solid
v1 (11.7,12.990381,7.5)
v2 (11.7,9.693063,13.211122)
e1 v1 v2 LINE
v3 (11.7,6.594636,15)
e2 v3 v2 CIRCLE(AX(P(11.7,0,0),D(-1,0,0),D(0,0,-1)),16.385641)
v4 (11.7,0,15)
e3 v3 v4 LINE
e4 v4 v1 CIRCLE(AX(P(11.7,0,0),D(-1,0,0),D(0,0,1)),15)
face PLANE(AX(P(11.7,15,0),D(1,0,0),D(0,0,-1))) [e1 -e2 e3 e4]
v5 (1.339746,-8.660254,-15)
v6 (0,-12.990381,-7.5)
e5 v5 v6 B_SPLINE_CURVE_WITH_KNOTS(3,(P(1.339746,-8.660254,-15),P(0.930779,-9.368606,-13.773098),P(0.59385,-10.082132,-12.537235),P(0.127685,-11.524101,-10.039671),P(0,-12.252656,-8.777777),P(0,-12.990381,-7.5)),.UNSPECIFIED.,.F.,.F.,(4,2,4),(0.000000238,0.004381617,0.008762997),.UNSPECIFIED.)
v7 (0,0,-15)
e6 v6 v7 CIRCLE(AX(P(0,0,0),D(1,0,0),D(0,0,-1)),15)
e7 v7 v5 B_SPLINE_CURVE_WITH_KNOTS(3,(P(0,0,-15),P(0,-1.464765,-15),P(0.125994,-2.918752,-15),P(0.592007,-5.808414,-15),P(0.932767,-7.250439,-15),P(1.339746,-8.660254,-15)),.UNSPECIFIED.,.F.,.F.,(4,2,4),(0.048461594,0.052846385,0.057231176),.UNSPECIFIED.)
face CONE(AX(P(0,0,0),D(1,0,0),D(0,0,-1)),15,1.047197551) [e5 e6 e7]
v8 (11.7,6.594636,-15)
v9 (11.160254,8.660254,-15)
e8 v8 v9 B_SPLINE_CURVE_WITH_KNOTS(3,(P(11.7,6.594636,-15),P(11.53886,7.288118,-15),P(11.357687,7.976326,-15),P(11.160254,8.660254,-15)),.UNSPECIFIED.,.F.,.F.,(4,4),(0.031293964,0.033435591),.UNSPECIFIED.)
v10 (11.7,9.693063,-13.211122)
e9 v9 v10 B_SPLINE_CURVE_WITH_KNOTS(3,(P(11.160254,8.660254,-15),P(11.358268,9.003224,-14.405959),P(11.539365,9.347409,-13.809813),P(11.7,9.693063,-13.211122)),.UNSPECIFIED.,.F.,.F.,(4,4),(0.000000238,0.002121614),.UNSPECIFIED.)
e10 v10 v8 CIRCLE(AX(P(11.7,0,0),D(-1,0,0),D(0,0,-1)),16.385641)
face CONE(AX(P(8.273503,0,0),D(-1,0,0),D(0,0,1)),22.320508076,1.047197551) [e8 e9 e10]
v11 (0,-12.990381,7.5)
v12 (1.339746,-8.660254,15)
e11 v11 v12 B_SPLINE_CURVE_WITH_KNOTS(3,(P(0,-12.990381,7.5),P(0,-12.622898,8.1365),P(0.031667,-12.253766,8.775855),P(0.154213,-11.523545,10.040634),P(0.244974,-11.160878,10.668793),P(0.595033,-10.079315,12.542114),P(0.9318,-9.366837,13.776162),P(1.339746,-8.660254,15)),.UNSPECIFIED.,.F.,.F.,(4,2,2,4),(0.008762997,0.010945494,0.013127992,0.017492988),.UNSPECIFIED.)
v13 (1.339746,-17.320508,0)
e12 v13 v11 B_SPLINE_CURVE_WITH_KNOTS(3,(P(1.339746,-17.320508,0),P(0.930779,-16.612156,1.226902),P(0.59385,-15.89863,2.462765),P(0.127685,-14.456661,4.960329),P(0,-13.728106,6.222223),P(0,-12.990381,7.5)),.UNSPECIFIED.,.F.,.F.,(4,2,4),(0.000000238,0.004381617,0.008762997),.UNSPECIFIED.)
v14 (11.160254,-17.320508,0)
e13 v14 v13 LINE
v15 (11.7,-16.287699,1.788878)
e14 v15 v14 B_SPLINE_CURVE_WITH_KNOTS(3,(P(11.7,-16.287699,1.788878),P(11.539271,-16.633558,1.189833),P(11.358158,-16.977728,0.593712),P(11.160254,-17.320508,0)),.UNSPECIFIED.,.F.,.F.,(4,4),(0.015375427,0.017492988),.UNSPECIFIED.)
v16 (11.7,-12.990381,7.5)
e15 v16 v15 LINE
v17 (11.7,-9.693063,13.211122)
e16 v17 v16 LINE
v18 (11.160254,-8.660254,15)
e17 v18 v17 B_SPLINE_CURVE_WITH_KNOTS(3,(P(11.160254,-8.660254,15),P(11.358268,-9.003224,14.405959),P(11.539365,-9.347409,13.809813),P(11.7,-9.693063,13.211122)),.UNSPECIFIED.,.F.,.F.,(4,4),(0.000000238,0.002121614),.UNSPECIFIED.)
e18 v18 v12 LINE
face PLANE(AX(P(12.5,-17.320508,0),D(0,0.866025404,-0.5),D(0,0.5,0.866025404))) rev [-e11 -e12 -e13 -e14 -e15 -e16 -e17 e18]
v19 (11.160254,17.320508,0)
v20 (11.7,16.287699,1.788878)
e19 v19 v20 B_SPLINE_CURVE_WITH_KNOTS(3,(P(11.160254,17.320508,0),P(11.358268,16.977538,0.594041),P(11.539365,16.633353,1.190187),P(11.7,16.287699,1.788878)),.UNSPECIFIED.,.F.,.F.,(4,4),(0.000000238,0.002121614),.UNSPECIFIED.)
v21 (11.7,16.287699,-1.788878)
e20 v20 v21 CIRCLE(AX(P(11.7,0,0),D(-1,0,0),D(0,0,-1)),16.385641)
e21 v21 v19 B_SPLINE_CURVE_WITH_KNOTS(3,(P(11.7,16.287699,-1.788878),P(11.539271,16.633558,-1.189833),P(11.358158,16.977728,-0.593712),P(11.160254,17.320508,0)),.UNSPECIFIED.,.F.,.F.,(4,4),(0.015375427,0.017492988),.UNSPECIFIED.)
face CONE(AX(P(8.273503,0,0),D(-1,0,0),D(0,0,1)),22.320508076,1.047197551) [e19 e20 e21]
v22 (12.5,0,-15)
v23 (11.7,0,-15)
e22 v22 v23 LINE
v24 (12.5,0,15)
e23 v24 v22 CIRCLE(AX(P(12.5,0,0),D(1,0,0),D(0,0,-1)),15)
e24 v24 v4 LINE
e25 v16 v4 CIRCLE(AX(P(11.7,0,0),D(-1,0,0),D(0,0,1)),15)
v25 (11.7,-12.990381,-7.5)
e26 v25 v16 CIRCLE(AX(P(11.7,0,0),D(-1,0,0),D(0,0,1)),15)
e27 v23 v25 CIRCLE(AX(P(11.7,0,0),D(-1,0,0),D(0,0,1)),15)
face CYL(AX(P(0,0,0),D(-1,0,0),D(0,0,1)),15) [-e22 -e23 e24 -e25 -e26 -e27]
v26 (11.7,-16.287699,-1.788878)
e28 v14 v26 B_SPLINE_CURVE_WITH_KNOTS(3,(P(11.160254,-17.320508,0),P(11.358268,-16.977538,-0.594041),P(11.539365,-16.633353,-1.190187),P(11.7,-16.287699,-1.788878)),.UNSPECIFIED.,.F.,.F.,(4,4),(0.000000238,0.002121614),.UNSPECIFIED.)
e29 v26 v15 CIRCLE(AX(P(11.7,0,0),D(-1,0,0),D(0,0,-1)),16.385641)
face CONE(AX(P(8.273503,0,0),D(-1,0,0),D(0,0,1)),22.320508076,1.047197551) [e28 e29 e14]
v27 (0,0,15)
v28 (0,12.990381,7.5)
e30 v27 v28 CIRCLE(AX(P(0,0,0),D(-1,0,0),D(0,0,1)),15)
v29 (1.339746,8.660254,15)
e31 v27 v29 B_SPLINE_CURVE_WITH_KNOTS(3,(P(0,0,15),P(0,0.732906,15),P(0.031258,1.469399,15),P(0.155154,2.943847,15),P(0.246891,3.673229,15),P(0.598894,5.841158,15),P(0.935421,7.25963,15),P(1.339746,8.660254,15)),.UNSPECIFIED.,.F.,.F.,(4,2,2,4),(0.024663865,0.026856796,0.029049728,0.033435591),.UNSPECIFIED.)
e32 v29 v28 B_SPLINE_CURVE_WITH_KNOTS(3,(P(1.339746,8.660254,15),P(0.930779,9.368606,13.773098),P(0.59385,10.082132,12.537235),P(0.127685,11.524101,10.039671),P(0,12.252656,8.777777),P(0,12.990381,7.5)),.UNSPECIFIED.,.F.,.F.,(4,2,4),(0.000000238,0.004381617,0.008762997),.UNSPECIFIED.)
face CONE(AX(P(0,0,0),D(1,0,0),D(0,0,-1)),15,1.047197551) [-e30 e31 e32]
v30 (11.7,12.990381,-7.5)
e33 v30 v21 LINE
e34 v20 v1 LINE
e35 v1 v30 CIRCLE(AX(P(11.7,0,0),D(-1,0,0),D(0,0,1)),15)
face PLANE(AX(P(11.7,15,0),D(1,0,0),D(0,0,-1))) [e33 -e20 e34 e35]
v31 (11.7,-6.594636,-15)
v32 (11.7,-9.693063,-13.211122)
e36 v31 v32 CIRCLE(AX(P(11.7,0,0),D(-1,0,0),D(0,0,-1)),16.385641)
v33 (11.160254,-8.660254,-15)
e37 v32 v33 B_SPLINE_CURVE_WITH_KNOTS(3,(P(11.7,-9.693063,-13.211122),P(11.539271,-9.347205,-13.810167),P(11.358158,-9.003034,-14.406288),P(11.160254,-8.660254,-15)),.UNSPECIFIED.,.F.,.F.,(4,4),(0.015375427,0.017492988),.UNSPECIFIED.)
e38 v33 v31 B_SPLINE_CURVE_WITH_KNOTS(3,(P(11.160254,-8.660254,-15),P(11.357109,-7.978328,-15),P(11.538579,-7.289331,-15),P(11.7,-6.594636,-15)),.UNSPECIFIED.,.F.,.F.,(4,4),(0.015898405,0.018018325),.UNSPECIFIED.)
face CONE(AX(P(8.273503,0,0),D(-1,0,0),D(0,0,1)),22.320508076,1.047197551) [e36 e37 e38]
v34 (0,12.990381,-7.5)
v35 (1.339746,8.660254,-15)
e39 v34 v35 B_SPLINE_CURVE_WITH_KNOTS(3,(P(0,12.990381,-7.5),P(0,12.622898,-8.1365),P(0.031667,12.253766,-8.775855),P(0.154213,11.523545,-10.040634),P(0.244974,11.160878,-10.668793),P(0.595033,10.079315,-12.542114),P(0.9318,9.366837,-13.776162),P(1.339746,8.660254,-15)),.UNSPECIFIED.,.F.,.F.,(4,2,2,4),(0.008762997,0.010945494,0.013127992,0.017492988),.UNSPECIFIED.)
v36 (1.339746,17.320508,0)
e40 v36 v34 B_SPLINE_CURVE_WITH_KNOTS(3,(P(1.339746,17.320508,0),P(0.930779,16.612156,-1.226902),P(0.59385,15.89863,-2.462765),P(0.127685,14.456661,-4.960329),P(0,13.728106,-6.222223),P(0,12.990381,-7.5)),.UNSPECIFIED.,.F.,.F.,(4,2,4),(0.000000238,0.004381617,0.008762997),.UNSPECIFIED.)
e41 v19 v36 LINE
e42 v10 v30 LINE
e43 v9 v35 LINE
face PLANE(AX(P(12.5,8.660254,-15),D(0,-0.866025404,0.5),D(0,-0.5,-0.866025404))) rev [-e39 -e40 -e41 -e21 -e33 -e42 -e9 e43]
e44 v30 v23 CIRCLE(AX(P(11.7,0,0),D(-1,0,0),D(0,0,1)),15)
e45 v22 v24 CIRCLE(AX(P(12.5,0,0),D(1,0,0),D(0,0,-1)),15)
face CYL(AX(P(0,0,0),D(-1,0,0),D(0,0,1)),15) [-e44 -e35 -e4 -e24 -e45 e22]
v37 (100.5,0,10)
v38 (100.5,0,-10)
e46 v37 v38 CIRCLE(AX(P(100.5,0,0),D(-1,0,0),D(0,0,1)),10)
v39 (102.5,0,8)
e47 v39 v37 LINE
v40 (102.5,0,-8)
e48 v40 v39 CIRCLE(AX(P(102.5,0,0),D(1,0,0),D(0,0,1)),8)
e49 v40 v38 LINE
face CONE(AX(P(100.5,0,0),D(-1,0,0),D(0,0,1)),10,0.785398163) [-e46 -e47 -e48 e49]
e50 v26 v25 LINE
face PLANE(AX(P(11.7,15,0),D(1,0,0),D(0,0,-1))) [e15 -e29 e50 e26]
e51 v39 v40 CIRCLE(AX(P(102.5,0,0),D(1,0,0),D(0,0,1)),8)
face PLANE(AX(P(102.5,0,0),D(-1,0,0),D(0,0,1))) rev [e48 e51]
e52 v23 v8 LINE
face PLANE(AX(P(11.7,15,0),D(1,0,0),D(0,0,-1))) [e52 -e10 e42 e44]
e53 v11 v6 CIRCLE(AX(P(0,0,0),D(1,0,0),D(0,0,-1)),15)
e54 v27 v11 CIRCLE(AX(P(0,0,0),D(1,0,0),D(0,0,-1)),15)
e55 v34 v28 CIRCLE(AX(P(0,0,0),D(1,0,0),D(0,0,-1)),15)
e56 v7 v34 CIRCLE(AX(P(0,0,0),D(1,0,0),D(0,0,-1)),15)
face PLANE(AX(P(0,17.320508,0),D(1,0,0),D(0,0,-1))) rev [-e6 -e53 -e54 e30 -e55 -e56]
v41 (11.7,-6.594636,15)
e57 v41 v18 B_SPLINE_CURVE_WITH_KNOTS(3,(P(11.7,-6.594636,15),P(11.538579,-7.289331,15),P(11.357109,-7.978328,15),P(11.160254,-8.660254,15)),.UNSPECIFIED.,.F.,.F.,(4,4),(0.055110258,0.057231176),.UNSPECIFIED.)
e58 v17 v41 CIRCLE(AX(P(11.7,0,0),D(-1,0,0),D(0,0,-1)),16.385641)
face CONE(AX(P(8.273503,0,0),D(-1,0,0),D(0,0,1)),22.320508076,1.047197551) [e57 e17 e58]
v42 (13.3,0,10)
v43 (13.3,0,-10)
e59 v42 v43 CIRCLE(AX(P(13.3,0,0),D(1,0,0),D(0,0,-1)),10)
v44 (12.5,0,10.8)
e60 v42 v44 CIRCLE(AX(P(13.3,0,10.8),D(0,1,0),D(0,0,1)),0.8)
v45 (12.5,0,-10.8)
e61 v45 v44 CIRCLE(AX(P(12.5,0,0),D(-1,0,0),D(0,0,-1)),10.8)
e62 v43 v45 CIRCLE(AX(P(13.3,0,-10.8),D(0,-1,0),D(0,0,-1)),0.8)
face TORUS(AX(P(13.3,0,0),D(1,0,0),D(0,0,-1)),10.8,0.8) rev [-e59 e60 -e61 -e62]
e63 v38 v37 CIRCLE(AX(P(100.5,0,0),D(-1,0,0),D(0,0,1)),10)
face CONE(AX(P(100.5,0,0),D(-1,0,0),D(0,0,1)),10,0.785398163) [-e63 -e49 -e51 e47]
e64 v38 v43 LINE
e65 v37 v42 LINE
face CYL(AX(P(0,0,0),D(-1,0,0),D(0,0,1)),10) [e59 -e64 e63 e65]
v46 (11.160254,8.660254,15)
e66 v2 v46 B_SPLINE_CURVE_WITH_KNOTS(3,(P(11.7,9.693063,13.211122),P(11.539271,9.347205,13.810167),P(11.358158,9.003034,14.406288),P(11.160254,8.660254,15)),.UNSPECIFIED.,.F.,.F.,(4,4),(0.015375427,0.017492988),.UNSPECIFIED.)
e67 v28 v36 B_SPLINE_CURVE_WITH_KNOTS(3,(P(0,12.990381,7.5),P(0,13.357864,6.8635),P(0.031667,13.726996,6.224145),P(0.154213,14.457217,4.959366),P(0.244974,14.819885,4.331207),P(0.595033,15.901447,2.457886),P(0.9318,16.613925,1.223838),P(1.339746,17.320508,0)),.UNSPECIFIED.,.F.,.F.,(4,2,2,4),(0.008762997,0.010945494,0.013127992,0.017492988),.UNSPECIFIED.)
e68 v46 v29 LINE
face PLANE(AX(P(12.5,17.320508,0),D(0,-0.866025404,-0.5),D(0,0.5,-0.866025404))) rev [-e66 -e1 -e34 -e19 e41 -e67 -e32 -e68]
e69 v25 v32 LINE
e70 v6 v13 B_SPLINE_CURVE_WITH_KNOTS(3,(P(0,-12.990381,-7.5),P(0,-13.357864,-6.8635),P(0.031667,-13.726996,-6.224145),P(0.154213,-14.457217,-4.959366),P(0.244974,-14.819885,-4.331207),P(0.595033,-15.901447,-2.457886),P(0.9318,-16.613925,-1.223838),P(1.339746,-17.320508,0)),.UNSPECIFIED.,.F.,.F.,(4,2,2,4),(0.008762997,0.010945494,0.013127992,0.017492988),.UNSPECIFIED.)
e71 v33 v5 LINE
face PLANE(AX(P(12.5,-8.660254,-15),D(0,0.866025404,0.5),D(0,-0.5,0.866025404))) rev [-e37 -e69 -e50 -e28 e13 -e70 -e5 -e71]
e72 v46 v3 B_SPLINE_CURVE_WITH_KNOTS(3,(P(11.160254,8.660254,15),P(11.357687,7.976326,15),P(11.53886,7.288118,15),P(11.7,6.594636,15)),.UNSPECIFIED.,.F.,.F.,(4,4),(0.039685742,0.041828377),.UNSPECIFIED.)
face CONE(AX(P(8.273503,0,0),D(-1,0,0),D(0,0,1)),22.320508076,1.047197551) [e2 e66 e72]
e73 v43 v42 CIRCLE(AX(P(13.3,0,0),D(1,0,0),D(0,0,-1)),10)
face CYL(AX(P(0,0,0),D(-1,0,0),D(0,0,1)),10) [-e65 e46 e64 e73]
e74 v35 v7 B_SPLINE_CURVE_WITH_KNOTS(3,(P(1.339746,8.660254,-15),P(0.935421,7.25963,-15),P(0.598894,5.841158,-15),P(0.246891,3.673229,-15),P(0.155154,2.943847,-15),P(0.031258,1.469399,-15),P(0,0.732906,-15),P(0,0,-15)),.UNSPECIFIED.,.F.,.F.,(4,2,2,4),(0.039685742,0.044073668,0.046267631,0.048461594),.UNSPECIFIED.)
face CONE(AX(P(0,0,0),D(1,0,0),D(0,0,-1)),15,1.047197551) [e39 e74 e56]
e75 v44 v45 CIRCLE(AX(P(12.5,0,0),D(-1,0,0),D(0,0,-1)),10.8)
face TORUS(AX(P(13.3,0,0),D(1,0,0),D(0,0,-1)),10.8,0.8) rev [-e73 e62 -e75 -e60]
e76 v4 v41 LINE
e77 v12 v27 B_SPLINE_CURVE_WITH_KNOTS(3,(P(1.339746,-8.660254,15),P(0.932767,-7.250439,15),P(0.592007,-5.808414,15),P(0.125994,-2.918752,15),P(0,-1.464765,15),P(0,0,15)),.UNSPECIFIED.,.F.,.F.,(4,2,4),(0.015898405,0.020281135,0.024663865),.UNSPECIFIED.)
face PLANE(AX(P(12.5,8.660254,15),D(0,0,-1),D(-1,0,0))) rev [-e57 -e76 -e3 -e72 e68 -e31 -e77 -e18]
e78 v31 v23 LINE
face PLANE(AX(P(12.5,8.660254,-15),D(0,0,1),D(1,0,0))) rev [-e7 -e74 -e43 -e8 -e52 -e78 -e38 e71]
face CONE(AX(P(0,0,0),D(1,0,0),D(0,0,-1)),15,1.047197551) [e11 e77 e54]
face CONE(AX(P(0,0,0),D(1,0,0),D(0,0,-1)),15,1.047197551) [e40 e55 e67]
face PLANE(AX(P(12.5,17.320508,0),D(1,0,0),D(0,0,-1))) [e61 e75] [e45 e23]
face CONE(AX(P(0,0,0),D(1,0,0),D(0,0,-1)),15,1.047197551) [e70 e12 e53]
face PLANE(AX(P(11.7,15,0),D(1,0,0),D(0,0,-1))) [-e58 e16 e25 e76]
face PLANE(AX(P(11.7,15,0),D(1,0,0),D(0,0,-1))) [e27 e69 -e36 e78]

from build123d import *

# Parameters (mm, degrees)
EXTRUDE_365_DEPTH = 12.5
SKETCH_4_W        = 0.8
SKETCH_4_H        = 12.320508076
CHAMFER_2074_SIZE = 2
FILLET_2128_R     = 0.8


with BuildPart() as part:
    # 草图1 → Extrude 365 (new body)
    with BuildSketch(Plane(origin=(0, 0, 0), x_dir=(0, 0, -1), z_dir=(1, 0, 0))):
        Polygon((15, 8.660254038), (15, -8.660254038), (0, -17.320508076), (-15, -8.660254038), (-15, 8.660254038), (0, 17.320508076), align=None)
    extrude(amount=EXTRUDE_365_DEPTH)

    # 草图2 → 凸台-旋转1 (revolve)
    with BuildSketch(Plane.XY, mode=Mode.PRIVATE) as revolve_1_sk:
        Polygon((0, 0), (102.5, 0), (102.5, 7.835), (102.5, 10), (7.791693541, 10), (0, 10), align=None)
    revolve(revolve_1_sk.sketch.rotate(Axis((0, 0, 0), (1, 0, 0)), 90), axis=Axis((0, 0, 0), (1, 0, 0)))

    # 草图3 → 切除-旋转1 (revolve, cut)
    with BuildSketch(Plane.XY):
        Polygon((0, 15), (4.226497308, 22.320508076), (4.226497308, 27.320508076), (-10, 27.320508076), (-10, 15), align=None)
    revolve(axis=Axis((0, 0, 0), (1, 0, 0)), mode=Mode.SUBTRACT)

    # 草图5 → 切除-旋转2 (revolve, cut)
    with BuildSketch(Plane.XY):
        Polygon((12.5, 15), (8.273502692, 22.320508076), (8.273502692, 27.320508076), (18.273502692, 27.320508076), (18.273502692, 15), align=None)
    revolve(axis=Axis((0, 0, 0), (1, 0, 0)), mode=Mode.SUBTRACT)

    # 草图4 → 切除-旋转3 (revolve, cut)
    with BuildSketch(Plane.XY, mode=Mode.PRIVATE) as cut_revolve_3_sk:
        with Locations((12.1, 21.160254038)):
            Rectangle(SKETCH_4_W, SKETCH_4_H)
    revolve(cut_revolve_3_sk.sketch.rotate(Axis((0, 0, 0), (1, 0, 0)), 270), axis=Axis((0, 0, 0), (1, 0, 0)), mode=Mode.SUBTRACT)

    # Chamfer 2074
    chamfer_2074_edges = [part.edges().sort_by_distance(p)[0] for p in [
        (102.5, 0, -10),
    ]]
    chamfer(chamfer_2074_edges, length=CHAMFER_2074_SIZE)

    # Fillet 2128
    fillet_2128_edges = [part.edges().sort_by_distance(p)[0] for p in [
        (12.5, 0, -10),
    ]]
    fillet(fillet_2128_edges, radius=FILLET_2128_R)


solid = part.part
